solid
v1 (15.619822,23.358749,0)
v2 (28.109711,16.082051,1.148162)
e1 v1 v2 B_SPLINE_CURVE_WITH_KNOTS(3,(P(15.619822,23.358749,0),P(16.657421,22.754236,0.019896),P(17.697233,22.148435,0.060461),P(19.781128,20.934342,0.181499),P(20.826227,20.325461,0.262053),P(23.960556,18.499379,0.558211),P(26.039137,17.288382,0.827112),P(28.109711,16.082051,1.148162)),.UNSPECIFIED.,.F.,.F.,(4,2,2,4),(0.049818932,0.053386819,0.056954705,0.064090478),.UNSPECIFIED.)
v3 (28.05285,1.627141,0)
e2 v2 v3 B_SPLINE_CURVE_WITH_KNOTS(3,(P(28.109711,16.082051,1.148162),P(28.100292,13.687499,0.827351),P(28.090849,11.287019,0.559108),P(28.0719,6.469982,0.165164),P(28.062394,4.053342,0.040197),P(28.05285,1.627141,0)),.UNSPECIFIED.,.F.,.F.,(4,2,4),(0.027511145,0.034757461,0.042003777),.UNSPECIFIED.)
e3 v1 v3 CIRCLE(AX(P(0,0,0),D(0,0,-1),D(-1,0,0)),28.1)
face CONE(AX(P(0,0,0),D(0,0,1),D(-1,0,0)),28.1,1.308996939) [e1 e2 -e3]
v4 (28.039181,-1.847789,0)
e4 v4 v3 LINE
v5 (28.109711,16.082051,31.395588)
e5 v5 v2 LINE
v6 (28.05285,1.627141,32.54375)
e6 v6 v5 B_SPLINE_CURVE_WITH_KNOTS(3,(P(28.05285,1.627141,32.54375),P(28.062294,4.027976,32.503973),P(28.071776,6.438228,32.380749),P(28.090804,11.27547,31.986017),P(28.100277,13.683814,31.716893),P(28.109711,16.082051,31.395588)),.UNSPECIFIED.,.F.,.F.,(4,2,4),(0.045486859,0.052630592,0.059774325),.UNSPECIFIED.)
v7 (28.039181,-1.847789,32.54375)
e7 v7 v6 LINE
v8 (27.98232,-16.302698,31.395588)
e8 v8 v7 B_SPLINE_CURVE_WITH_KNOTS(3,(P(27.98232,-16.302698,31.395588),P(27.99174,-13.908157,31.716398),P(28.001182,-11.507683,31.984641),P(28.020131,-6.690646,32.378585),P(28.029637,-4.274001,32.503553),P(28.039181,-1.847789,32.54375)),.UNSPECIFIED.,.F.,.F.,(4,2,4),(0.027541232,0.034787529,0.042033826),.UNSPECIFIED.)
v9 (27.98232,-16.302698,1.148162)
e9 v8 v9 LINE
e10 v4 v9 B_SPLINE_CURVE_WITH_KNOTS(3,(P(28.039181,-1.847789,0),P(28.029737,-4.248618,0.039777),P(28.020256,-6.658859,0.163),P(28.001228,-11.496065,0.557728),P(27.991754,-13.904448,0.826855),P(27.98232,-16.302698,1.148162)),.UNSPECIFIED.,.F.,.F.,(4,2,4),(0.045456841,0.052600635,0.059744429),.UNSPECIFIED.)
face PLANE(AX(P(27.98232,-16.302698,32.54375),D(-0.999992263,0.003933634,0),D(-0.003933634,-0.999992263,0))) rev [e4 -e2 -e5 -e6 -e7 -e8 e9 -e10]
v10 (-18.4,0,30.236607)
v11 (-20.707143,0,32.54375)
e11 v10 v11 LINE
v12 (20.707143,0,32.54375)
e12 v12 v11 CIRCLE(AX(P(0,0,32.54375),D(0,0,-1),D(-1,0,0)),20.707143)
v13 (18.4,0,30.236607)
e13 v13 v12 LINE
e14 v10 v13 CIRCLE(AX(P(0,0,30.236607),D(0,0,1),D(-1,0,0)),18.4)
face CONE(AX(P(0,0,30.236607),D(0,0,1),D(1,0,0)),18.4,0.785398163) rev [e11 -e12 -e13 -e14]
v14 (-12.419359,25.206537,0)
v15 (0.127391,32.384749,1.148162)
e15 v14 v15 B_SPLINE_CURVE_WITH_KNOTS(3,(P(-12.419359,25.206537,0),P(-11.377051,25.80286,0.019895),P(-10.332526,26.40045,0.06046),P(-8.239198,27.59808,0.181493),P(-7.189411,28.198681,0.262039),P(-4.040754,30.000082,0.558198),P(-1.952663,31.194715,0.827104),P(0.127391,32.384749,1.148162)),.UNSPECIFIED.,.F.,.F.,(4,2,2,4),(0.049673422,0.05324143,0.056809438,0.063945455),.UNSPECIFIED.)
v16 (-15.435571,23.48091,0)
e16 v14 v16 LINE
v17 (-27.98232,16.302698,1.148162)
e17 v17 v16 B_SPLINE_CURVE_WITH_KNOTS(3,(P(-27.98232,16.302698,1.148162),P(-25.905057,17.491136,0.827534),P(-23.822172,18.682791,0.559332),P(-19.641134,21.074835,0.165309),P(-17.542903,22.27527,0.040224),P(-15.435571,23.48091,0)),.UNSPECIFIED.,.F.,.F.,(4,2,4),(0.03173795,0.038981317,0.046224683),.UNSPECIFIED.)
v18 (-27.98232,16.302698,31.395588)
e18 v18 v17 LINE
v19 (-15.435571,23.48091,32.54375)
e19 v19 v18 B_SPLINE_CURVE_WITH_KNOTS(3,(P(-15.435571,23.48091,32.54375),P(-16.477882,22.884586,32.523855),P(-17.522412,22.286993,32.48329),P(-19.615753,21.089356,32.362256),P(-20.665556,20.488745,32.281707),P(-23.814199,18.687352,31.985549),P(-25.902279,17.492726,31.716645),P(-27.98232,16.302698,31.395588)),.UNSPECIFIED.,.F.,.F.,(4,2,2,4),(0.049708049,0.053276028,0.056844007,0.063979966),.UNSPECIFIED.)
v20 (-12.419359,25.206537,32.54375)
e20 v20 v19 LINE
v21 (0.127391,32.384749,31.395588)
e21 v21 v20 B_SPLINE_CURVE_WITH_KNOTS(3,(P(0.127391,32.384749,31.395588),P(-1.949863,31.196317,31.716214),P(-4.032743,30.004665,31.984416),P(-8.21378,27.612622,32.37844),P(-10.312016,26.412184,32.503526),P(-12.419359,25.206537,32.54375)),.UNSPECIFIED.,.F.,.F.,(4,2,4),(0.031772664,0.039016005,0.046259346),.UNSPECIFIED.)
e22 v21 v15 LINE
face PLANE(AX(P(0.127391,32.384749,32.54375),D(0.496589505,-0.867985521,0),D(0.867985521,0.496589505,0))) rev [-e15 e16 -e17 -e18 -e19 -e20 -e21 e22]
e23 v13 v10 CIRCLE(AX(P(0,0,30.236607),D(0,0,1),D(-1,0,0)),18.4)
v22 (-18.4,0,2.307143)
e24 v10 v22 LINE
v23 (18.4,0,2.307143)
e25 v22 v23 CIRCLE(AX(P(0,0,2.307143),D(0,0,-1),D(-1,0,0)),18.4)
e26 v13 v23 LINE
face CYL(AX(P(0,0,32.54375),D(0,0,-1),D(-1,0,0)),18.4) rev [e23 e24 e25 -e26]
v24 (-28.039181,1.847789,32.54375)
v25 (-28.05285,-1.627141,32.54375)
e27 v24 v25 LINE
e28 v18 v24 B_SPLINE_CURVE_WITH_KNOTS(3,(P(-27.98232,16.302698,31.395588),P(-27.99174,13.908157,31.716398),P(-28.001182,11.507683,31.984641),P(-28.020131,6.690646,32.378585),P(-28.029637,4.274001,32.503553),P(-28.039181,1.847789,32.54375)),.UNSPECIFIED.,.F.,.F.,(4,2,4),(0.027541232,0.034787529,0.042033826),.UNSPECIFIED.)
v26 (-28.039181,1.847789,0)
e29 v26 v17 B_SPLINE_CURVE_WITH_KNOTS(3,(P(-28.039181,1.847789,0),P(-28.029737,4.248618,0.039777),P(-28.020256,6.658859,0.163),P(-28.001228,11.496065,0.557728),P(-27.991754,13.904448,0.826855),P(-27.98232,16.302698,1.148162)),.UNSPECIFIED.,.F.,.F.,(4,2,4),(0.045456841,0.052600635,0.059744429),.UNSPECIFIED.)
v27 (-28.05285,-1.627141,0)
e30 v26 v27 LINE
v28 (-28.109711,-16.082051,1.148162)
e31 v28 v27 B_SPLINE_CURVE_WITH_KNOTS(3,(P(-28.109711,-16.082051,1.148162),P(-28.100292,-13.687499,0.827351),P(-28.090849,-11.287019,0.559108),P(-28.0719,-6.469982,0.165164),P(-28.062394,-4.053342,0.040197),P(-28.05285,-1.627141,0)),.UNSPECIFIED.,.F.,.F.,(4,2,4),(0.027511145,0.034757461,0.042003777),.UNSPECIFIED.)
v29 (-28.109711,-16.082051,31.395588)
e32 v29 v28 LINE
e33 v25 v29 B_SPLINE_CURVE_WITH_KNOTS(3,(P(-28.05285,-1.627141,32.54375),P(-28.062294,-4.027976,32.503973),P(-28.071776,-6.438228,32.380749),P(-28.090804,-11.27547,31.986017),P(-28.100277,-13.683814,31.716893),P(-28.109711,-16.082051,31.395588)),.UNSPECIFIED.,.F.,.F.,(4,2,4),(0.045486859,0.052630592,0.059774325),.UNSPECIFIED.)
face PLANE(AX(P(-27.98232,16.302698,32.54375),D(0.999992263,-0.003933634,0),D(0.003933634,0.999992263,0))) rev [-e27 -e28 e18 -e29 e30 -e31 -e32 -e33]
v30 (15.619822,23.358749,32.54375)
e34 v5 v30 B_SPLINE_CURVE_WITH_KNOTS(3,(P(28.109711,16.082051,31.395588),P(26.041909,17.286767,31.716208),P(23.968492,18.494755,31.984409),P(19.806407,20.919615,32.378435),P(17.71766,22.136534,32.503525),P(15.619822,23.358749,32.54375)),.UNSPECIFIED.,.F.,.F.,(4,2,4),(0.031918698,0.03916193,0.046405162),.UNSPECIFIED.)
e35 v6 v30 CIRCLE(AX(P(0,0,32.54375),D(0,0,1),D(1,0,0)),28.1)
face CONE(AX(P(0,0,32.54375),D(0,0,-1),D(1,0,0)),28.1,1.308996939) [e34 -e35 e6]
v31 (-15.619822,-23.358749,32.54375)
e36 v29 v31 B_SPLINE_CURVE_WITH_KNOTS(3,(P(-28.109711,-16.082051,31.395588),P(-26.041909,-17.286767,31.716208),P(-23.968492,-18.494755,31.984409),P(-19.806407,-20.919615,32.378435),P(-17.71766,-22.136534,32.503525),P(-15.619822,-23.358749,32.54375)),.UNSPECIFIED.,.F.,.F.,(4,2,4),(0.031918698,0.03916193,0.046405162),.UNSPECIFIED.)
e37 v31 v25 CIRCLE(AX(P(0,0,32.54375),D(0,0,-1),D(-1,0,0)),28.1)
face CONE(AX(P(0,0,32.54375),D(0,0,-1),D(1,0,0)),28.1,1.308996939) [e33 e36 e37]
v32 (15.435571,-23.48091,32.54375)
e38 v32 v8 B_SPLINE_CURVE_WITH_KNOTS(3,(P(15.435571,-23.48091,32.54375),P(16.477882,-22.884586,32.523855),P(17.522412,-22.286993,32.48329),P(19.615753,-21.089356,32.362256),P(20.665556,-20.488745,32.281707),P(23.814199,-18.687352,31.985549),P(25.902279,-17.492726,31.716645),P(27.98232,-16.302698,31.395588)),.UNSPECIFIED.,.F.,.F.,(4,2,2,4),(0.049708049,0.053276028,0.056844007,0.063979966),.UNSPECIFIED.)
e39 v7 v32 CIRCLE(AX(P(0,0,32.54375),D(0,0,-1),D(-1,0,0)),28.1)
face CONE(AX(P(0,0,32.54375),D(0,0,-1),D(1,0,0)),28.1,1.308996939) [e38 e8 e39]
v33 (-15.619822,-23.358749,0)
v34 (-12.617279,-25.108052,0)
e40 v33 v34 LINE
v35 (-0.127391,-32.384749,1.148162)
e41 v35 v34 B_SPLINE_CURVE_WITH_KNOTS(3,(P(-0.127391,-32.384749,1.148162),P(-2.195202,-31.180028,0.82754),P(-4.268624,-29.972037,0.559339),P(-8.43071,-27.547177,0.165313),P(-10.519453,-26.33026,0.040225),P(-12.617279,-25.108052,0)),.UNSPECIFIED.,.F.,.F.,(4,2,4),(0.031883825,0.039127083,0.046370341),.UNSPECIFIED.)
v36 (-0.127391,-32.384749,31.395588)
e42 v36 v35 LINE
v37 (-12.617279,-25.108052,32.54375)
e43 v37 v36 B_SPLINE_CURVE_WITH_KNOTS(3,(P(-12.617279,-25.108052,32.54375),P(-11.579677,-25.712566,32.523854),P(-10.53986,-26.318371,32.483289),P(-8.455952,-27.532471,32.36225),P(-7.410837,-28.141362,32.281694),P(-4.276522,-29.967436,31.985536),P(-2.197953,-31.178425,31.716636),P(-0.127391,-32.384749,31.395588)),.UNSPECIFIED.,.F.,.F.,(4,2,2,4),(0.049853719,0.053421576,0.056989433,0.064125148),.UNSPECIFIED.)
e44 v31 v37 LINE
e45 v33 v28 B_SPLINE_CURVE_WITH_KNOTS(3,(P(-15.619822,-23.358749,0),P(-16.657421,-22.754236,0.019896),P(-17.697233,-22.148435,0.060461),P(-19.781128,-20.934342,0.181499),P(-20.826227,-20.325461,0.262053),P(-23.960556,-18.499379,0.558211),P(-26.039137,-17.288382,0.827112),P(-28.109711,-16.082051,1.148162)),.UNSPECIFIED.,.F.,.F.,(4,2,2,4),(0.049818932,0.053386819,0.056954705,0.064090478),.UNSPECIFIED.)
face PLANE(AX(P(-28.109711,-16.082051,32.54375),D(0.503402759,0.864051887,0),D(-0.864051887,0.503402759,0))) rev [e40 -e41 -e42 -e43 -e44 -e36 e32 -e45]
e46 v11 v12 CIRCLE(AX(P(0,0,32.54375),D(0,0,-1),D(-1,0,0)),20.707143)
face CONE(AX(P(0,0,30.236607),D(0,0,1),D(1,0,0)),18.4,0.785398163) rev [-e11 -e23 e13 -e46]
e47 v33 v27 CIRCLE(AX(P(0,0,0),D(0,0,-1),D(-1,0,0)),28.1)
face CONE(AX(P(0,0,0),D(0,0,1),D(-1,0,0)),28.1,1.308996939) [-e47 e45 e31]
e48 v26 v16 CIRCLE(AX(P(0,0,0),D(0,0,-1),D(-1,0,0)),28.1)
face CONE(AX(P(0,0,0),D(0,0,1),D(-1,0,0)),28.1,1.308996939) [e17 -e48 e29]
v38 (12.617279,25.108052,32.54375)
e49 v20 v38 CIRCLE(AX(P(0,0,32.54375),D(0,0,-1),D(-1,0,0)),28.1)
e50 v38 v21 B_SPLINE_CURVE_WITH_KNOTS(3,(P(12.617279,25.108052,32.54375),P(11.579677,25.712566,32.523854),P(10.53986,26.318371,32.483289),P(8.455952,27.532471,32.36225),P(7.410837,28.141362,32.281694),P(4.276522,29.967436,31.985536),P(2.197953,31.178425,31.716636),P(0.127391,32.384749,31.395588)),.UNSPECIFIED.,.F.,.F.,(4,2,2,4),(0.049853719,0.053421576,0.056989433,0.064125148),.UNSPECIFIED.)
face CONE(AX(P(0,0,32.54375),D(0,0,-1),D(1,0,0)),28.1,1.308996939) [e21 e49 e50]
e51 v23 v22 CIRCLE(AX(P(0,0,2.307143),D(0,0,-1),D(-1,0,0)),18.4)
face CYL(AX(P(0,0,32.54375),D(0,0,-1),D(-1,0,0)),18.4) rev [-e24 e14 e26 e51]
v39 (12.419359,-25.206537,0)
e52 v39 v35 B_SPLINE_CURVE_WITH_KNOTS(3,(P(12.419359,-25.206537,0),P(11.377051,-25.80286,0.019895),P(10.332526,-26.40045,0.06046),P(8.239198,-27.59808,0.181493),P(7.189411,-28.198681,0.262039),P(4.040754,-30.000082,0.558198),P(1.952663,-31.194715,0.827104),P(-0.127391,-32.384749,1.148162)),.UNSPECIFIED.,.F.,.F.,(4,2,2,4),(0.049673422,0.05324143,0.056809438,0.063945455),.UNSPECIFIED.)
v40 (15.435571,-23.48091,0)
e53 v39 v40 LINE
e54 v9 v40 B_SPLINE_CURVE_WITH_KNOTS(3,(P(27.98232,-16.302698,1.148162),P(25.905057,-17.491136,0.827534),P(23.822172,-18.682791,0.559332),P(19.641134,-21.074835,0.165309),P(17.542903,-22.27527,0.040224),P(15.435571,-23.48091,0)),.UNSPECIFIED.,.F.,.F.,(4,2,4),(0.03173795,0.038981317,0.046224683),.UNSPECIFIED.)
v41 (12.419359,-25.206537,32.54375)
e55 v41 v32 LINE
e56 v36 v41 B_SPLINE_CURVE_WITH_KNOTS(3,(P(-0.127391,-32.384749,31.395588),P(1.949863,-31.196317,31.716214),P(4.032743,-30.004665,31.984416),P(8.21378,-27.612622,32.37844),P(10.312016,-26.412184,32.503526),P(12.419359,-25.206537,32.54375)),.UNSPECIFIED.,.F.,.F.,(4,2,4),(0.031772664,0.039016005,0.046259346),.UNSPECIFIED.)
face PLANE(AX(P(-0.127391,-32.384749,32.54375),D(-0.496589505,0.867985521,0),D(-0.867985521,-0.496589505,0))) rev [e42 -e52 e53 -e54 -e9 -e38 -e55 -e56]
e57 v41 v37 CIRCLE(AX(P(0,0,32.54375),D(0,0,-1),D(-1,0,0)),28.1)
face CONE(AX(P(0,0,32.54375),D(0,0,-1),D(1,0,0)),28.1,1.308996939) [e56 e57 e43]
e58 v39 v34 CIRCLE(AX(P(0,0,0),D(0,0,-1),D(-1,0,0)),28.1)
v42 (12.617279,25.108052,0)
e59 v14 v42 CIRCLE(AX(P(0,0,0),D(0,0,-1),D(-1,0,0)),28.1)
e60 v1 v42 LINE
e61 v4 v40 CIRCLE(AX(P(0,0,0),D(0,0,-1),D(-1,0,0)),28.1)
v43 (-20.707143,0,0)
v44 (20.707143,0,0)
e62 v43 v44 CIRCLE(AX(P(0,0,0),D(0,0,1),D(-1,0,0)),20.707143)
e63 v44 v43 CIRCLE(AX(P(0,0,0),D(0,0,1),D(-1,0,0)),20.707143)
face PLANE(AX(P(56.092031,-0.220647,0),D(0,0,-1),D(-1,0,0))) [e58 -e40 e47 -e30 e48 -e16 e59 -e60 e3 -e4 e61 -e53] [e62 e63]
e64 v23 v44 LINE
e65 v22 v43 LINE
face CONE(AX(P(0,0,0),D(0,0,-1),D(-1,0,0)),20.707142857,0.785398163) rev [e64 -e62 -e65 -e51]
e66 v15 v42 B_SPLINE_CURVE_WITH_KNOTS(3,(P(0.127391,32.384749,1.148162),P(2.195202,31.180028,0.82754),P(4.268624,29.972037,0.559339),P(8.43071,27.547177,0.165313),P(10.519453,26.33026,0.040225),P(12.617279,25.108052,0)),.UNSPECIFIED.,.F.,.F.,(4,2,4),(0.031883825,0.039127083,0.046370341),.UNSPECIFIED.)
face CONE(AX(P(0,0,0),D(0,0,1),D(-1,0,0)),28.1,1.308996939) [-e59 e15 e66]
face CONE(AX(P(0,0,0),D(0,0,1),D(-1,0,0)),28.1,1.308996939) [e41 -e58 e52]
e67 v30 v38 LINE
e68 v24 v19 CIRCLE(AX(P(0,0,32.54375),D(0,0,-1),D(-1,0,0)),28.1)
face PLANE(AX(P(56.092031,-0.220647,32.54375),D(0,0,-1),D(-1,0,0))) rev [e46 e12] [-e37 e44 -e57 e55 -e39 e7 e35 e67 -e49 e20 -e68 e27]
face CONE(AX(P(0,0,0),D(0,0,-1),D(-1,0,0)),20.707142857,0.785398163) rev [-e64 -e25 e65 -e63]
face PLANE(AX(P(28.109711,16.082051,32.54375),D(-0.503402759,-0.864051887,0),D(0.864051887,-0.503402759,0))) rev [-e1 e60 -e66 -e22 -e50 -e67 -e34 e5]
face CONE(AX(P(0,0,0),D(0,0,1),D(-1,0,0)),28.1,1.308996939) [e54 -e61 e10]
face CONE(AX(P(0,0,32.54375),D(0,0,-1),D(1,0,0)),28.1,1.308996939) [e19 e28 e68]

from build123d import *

# Parameters (mm, degrees)
SKETCH1_R          = 18.4
BASE_EXTRUDE_DEPTH = 32.54375
SKETCH2_OUTSIDE_W  = 485.848
SKETCH2_OUTSIDE_H  = 494.398
SKETCH2_OUTSIDE_R  = 28.1
CUT_EXTRUDE1_DEPTH = 54.833293767
CUT_EXTRUDE1_DRAFT = -75
SKETCH3_OUTSIDE_W  = 485.848
SKETCH3_OUTSIDE_H  = 494.398
SKETCH3_OUTSIDE_R  = 28.1
CUT_EXTRUDE2_DEPTH = 54.833293767
CUT_EXTRUDE2_DRAFT = -75
CHAMFER1_SIZE      = 2.307142857


with BuildPart() as part:
    # Sketch1 → Base-Extrude (new body)
    with BuildSketch(Plane.XY):
        Polygon((0.127390736, 32.384749445), (-27.982320346, 16.302698336), (-28.109711083, -16.082051108), (-0.127390736, -32.384749445), (27.982320346, -16.302698336), (28.109711083, 16.082051108), align=None)
        Circle(SKETCH1_R, mode=Mode.SUBTRACT)
    extrude(amount=BASE_EXTRUDE_DEPTH)


with BuildPart() as cut_extrude1_tool:
    # Sketch2 outside → Cut-Extrude1 (with draft: the straight prism first)
    with BuildSketch(Plane(origin=(0, 0, 0), x_dir=(-1, 0, 0), z_dir=(0, 0, -1))):
        Rectangle(SKETCH2_OUTSIDE_W, SKETCH2_OUTSIDE_H)
        Circle(SKETCH2_OUTSIDE_R, mode=Mode.SUBTRACT)
    extrude(amount=-CUT_EXTRUDE1_DEPTH)
    # Cut-Extrude1: the draft: its side faces are tilted about the plane it starts from
    cut_extrude1_sides = [cut_extrude1_tool.faces().sort_by_distance(p)[0] for p in [
        (0, -247.199, 27.416646884),
        (-242.924, 0, 27.416646884),
        (0, 247.199, 27.416646884),
        (242.924, 0, 27.416646884),
        (28.1, 0, 27.416646884),
    ]]
    draft(cut_extrude1_sides, Plane(origin=(0, 0, 0), x_dir=(-1, 0, 0), z_dir=(0, 0, -1)), CUT_EXTRUDE1_DRAFT)


with BuildPart() as part_1:
    add(part.part)

    # Cut-Extrude1: cut by cut_extrude1_tool
    add(cut_extrude1_tool.part, mode=Mode.SUBTRACT)


with BuildPart() as cut_extrude2_tool:
    # Sketch3 outside → Cut-Extrude2 (with draft: the straight prism first)
    with BuildSketch(Plane.XY.offset(32.54375)):
        Rectangle(SKETCH3_OUTSIDE_W, SKETCH3_OUTSIDE_H)
        Circle(SKETCH3_OUTSIDE_R, mode=Mode.SUBTRACT)
    extrude(amount=-CUT_EXTRUDE2_DEPTH)
    # Cut-Extrude2: the draft: its side faces are tilted about the plane it starts from
    cut_extrude2_sides = [cut_extrude2_tool.faces().sort_by_distance(p)[0] for p in [
        (0, -247.199, 5.127103116),
        (242.924, 0, 5.127103116),
        (0, 247.199, 5.127103116),
        (-242.924, 0, 5.127103116),
        (-28.1, 0, 5.127103116),
    ]]
    draft(cut_extrude2_sides, Plane.XY.offset(32.54375), CUT_EXTRUDE2_DRAFT)


with BuildPart() as part_2:
    add(part_1.part)

    # Cut-Extrude2: cut by cut_extrude2_tool
    add(cut_extrude2_tool.part, mode=Mode.SUBTRACT)

    # Chamfer1
    chamfer1_edges = [part_2.edges().sort_by_distance(p)[0] for p in [
        (-18.4, 0, 0),
        (-18.4, 0, 32.54375),
    ]]
    chamfer(chamfer1_edges, length=CHAMFER1_SIZE)


solid = part_2.part
